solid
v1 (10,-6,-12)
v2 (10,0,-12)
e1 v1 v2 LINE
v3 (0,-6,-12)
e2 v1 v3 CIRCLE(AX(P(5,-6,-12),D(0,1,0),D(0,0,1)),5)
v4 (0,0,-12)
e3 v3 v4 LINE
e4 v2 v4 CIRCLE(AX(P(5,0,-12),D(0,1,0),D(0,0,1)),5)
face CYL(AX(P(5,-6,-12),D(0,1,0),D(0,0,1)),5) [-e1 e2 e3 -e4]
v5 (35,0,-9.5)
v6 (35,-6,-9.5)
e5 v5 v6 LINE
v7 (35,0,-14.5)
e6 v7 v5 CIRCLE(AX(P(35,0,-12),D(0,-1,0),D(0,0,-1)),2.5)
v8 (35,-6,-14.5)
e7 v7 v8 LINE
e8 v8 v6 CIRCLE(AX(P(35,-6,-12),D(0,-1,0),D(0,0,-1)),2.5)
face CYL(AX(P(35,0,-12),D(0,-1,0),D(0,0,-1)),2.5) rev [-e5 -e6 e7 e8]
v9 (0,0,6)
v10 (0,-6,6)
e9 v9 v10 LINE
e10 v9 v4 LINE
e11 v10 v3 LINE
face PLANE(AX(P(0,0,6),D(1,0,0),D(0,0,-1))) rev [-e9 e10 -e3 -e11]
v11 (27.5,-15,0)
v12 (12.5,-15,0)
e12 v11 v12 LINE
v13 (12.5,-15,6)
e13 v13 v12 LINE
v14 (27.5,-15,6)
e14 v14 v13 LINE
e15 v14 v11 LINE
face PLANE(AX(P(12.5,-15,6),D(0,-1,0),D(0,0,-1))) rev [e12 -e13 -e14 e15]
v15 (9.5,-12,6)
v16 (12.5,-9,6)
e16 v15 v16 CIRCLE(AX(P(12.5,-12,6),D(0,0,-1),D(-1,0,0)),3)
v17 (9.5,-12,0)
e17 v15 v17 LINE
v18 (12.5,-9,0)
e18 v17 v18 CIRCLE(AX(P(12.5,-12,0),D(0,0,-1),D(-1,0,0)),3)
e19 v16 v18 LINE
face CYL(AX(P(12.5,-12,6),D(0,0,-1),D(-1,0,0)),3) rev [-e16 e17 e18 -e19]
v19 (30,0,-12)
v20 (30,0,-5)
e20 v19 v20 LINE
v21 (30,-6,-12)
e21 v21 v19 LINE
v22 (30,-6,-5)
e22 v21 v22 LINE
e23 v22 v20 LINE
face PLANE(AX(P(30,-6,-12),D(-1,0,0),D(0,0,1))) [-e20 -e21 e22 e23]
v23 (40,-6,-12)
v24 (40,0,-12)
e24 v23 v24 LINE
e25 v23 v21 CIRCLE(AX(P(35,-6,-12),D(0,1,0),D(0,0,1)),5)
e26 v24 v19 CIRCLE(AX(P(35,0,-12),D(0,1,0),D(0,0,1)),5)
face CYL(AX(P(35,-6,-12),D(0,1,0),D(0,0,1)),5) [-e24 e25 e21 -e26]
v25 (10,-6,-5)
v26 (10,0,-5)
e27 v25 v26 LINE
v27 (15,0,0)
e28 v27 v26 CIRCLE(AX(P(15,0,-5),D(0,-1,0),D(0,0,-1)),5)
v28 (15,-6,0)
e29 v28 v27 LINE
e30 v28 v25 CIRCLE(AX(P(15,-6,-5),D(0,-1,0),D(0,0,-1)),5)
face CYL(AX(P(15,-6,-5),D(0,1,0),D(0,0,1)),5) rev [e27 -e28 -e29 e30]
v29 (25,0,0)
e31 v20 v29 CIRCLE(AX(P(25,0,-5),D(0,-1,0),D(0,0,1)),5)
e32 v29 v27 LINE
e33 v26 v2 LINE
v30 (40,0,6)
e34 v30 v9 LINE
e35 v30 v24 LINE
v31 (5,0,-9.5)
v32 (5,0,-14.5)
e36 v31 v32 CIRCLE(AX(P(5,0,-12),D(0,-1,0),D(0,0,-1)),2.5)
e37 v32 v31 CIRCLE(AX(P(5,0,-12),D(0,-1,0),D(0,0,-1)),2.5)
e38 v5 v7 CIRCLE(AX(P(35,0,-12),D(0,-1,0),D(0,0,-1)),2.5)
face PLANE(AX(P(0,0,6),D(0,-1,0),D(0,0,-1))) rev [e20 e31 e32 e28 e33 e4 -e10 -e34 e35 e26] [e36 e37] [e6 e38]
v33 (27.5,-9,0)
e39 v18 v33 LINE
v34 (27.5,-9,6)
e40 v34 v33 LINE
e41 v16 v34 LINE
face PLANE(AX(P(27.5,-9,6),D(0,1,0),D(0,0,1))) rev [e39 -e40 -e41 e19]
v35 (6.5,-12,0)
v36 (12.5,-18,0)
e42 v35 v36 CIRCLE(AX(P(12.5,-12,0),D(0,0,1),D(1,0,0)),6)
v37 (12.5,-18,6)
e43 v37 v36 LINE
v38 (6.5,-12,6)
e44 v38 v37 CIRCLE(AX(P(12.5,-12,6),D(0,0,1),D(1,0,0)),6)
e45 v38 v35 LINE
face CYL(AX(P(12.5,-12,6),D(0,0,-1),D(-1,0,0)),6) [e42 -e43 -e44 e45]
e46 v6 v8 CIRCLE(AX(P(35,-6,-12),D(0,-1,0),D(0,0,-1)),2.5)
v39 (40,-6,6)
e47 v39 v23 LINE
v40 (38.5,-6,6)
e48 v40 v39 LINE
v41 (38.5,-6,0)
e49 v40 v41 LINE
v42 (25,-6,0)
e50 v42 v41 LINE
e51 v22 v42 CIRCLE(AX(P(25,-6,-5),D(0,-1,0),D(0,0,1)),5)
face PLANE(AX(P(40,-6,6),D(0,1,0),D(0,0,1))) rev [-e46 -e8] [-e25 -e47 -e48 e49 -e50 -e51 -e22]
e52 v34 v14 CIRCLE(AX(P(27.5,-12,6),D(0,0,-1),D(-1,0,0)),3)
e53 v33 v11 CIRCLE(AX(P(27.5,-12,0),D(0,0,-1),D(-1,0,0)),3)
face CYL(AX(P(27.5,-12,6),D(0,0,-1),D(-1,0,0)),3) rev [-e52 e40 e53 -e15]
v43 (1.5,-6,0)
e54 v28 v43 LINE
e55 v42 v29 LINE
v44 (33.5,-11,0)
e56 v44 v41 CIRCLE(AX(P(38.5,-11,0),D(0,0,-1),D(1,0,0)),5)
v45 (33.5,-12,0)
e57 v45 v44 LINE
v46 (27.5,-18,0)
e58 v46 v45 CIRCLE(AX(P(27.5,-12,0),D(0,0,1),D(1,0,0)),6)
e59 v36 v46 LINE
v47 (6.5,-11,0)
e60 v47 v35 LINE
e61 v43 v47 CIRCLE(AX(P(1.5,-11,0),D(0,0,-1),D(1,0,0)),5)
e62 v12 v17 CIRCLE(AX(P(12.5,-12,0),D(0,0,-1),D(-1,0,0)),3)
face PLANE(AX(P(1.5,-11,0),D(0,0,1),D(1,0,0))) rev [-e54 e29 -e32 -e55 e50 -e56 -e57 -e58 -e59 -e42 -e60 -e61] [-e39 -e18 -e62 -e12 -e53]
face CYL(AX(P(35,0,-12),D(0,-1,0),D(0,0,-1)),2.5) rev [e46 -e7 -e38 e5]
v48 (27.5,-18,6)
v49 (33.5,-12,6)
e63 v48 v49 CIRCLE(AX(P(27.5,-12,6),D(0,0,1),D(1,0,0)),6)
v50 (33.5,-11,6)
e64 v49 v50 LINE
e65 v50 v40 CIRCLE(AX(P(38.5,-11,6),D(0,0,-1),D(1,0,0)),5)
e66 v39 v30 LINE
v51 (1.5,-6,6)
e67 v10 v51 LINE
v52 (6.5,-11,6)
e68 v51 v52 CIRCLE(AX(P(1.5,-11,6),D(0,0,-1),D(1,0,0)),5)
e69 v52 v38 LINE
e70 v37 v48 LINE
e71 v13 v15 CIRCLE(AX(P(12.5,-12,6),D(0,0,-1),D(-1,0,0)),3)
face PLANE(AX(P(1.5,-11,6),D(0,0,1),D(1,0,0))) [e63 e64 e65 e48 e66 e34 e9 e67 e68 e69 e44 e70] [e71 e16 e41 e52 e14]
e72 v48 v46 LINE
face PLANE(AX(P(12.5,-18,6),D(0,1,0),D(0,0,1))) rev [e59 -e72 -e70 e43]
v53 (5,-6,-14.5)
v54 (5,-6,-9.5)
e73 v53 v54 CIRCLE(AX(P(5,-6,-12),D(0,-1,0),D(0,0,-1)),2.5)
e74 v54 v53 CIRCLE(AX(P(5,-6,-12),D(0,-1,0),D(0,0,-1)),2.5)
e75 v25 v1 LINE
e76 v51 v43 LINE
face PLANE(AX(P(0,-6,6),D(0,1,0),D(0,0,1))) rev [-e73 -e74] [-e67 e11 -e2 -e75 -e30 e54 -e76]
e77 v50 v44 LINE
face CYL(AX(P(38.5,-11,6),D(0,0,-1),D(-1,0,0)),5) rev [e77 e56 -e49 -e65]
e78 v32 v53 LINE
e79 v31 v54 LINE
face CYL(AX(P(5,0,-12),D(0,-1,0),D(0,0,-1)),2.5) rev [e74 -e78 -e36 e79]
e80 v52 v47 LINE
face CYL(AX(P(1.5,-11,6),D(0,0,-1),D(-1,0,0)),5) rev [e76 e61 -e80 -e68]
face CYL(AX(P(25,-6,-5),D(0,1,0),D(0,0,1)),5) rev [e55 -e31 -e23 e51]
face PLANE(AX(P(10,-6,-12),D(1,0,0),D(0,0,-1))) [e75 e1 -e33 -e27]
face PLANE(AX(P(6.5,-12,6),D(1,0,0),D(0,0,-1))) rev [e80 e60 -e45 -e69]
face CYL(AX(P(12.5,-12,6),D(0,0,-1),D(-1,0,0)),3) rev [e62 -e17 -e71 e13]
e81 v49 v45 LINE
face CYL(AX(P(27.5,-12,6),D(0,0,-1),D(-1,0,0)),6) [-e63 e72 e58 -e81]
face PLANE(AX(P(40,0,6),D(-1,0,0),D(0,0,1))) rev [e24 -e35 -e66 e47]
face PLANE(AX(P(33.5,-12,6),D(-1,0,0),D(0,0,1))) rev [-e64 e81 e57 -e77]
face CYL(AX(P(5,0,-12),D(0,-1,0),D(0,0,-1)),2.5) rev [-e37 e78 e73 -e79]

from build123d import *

# Parameters (mm, degrees)
U_BRACKET_BASE_DEPTH    = 6
SLOTTED_TAB_DEPTH       = 6
MOUNTING_HOLES_SKETCH_R = 2.5
MOUNTING_HOLES_2X_DEPTH = 6
TAB_SLOT_DEPTH          = 6


with BuildPart() as part:
    # U Bracket Profile Sketch → U Bracket Base (new body)
    with BuildSketch(Plane.XY):
        with BuildLine():
            Line((0, 0), (40, 0))
            Line((40, 0), (40, -6))
            Line((40, -6), (38.5, -6))
            ThreePointArc((38.5, -6), (34.964466094, -7.464466094), (33.5, -11))
            Line((33.5, -11), (33.5, -12))
            ThreePointArc((33.5, -12), (31.742640687, -16.242640687), (27.5, -18))
            Line((27.5, -18), (12.5, -18))
            ThreePointArc((12.5, -18), (8.257359313, -16.242640687), (6.5, -12))
            Line((6.5, -12), (6.5, -11))
            ThreePointArc((6.5, -11), (5.035533906, -7.464466094), (1.5, -6))
            Line((1.5, -6), (0, -6))
            Line((0, -6), (0, 0))
        make_face()
    extrude(amount=U_BRACKET_BASE_DEPTH)

    # Slotted Tab Sketch → Slotted Tab (add)
    with BuildSketch(Plane(origin=(0, 0, 0), x_dir=(1, 0, 0), z_dir=(0, 1, 0))):
        with BuildLine():
            Line((0, 12), (0, 0))
            Line((0, 0), (15, 0))
            ThreePointArc((15, 0), (11.464466094, 1.464466094), (10, 5))
            Line((10, 5), (10, 12))
            ThreePointArc((10, 12), (5, 17), (0, 12))
        make_face()
        with BuildLine():
            Line((40, 12), (40, 0))
            Line((40, 0), (25, 0))
            ThreePointArc((25, 0), (28.535533906, 1.464466094), (30, 5))
            Line((30, 5), (30, 12))
            ThreePointArc((30, 12), (35, 17), (40, 12))
        make_face()
    extrude(amount=-SLOTTED_TAB_DEPTH)

    # Mounting Holes Sketch → Mounting Holes 2x (cut)
    with BuildSketch(Plane.XZ.offset(6)):
        with Locations(Location((5, -12, 0), (0, 0, 270))):
            Circle(MOUNTING_HOLES_SKETCH_R)
        with Locations(Location((35, -12, 0), (0, 0, 270))):
            Circle(MOUNTING_HOLES_SKETCH_R)
    extrude(amount=-MOUNTING_HOLES_2X_DEPTH, mode=Mode.SUBTRACT)

    # Tab Slot Sketch → Tab Slot (cut)
    with BuildSketch(Plane(origin=(0, 0, 0), x_dir=(-1, 0, 0), z_dir=(0, 0, -1))):
        with BuildLine():
            Line((-27.5, -9), (-12.5, -9))
            ThreePointArc((-12.5, -9), (-9.5, -12), (-12.5, -15))
            Line((-12.5, -15), (-27.5, -15))
            ThreePointArc((-27.5, -15), (-30.5, -12), (-27.5, -9))
        make_face()
    extrude(amount=-TAB_SLOT_DEPTH, mode=Mode.SUBTRACT)


solid = part.part
